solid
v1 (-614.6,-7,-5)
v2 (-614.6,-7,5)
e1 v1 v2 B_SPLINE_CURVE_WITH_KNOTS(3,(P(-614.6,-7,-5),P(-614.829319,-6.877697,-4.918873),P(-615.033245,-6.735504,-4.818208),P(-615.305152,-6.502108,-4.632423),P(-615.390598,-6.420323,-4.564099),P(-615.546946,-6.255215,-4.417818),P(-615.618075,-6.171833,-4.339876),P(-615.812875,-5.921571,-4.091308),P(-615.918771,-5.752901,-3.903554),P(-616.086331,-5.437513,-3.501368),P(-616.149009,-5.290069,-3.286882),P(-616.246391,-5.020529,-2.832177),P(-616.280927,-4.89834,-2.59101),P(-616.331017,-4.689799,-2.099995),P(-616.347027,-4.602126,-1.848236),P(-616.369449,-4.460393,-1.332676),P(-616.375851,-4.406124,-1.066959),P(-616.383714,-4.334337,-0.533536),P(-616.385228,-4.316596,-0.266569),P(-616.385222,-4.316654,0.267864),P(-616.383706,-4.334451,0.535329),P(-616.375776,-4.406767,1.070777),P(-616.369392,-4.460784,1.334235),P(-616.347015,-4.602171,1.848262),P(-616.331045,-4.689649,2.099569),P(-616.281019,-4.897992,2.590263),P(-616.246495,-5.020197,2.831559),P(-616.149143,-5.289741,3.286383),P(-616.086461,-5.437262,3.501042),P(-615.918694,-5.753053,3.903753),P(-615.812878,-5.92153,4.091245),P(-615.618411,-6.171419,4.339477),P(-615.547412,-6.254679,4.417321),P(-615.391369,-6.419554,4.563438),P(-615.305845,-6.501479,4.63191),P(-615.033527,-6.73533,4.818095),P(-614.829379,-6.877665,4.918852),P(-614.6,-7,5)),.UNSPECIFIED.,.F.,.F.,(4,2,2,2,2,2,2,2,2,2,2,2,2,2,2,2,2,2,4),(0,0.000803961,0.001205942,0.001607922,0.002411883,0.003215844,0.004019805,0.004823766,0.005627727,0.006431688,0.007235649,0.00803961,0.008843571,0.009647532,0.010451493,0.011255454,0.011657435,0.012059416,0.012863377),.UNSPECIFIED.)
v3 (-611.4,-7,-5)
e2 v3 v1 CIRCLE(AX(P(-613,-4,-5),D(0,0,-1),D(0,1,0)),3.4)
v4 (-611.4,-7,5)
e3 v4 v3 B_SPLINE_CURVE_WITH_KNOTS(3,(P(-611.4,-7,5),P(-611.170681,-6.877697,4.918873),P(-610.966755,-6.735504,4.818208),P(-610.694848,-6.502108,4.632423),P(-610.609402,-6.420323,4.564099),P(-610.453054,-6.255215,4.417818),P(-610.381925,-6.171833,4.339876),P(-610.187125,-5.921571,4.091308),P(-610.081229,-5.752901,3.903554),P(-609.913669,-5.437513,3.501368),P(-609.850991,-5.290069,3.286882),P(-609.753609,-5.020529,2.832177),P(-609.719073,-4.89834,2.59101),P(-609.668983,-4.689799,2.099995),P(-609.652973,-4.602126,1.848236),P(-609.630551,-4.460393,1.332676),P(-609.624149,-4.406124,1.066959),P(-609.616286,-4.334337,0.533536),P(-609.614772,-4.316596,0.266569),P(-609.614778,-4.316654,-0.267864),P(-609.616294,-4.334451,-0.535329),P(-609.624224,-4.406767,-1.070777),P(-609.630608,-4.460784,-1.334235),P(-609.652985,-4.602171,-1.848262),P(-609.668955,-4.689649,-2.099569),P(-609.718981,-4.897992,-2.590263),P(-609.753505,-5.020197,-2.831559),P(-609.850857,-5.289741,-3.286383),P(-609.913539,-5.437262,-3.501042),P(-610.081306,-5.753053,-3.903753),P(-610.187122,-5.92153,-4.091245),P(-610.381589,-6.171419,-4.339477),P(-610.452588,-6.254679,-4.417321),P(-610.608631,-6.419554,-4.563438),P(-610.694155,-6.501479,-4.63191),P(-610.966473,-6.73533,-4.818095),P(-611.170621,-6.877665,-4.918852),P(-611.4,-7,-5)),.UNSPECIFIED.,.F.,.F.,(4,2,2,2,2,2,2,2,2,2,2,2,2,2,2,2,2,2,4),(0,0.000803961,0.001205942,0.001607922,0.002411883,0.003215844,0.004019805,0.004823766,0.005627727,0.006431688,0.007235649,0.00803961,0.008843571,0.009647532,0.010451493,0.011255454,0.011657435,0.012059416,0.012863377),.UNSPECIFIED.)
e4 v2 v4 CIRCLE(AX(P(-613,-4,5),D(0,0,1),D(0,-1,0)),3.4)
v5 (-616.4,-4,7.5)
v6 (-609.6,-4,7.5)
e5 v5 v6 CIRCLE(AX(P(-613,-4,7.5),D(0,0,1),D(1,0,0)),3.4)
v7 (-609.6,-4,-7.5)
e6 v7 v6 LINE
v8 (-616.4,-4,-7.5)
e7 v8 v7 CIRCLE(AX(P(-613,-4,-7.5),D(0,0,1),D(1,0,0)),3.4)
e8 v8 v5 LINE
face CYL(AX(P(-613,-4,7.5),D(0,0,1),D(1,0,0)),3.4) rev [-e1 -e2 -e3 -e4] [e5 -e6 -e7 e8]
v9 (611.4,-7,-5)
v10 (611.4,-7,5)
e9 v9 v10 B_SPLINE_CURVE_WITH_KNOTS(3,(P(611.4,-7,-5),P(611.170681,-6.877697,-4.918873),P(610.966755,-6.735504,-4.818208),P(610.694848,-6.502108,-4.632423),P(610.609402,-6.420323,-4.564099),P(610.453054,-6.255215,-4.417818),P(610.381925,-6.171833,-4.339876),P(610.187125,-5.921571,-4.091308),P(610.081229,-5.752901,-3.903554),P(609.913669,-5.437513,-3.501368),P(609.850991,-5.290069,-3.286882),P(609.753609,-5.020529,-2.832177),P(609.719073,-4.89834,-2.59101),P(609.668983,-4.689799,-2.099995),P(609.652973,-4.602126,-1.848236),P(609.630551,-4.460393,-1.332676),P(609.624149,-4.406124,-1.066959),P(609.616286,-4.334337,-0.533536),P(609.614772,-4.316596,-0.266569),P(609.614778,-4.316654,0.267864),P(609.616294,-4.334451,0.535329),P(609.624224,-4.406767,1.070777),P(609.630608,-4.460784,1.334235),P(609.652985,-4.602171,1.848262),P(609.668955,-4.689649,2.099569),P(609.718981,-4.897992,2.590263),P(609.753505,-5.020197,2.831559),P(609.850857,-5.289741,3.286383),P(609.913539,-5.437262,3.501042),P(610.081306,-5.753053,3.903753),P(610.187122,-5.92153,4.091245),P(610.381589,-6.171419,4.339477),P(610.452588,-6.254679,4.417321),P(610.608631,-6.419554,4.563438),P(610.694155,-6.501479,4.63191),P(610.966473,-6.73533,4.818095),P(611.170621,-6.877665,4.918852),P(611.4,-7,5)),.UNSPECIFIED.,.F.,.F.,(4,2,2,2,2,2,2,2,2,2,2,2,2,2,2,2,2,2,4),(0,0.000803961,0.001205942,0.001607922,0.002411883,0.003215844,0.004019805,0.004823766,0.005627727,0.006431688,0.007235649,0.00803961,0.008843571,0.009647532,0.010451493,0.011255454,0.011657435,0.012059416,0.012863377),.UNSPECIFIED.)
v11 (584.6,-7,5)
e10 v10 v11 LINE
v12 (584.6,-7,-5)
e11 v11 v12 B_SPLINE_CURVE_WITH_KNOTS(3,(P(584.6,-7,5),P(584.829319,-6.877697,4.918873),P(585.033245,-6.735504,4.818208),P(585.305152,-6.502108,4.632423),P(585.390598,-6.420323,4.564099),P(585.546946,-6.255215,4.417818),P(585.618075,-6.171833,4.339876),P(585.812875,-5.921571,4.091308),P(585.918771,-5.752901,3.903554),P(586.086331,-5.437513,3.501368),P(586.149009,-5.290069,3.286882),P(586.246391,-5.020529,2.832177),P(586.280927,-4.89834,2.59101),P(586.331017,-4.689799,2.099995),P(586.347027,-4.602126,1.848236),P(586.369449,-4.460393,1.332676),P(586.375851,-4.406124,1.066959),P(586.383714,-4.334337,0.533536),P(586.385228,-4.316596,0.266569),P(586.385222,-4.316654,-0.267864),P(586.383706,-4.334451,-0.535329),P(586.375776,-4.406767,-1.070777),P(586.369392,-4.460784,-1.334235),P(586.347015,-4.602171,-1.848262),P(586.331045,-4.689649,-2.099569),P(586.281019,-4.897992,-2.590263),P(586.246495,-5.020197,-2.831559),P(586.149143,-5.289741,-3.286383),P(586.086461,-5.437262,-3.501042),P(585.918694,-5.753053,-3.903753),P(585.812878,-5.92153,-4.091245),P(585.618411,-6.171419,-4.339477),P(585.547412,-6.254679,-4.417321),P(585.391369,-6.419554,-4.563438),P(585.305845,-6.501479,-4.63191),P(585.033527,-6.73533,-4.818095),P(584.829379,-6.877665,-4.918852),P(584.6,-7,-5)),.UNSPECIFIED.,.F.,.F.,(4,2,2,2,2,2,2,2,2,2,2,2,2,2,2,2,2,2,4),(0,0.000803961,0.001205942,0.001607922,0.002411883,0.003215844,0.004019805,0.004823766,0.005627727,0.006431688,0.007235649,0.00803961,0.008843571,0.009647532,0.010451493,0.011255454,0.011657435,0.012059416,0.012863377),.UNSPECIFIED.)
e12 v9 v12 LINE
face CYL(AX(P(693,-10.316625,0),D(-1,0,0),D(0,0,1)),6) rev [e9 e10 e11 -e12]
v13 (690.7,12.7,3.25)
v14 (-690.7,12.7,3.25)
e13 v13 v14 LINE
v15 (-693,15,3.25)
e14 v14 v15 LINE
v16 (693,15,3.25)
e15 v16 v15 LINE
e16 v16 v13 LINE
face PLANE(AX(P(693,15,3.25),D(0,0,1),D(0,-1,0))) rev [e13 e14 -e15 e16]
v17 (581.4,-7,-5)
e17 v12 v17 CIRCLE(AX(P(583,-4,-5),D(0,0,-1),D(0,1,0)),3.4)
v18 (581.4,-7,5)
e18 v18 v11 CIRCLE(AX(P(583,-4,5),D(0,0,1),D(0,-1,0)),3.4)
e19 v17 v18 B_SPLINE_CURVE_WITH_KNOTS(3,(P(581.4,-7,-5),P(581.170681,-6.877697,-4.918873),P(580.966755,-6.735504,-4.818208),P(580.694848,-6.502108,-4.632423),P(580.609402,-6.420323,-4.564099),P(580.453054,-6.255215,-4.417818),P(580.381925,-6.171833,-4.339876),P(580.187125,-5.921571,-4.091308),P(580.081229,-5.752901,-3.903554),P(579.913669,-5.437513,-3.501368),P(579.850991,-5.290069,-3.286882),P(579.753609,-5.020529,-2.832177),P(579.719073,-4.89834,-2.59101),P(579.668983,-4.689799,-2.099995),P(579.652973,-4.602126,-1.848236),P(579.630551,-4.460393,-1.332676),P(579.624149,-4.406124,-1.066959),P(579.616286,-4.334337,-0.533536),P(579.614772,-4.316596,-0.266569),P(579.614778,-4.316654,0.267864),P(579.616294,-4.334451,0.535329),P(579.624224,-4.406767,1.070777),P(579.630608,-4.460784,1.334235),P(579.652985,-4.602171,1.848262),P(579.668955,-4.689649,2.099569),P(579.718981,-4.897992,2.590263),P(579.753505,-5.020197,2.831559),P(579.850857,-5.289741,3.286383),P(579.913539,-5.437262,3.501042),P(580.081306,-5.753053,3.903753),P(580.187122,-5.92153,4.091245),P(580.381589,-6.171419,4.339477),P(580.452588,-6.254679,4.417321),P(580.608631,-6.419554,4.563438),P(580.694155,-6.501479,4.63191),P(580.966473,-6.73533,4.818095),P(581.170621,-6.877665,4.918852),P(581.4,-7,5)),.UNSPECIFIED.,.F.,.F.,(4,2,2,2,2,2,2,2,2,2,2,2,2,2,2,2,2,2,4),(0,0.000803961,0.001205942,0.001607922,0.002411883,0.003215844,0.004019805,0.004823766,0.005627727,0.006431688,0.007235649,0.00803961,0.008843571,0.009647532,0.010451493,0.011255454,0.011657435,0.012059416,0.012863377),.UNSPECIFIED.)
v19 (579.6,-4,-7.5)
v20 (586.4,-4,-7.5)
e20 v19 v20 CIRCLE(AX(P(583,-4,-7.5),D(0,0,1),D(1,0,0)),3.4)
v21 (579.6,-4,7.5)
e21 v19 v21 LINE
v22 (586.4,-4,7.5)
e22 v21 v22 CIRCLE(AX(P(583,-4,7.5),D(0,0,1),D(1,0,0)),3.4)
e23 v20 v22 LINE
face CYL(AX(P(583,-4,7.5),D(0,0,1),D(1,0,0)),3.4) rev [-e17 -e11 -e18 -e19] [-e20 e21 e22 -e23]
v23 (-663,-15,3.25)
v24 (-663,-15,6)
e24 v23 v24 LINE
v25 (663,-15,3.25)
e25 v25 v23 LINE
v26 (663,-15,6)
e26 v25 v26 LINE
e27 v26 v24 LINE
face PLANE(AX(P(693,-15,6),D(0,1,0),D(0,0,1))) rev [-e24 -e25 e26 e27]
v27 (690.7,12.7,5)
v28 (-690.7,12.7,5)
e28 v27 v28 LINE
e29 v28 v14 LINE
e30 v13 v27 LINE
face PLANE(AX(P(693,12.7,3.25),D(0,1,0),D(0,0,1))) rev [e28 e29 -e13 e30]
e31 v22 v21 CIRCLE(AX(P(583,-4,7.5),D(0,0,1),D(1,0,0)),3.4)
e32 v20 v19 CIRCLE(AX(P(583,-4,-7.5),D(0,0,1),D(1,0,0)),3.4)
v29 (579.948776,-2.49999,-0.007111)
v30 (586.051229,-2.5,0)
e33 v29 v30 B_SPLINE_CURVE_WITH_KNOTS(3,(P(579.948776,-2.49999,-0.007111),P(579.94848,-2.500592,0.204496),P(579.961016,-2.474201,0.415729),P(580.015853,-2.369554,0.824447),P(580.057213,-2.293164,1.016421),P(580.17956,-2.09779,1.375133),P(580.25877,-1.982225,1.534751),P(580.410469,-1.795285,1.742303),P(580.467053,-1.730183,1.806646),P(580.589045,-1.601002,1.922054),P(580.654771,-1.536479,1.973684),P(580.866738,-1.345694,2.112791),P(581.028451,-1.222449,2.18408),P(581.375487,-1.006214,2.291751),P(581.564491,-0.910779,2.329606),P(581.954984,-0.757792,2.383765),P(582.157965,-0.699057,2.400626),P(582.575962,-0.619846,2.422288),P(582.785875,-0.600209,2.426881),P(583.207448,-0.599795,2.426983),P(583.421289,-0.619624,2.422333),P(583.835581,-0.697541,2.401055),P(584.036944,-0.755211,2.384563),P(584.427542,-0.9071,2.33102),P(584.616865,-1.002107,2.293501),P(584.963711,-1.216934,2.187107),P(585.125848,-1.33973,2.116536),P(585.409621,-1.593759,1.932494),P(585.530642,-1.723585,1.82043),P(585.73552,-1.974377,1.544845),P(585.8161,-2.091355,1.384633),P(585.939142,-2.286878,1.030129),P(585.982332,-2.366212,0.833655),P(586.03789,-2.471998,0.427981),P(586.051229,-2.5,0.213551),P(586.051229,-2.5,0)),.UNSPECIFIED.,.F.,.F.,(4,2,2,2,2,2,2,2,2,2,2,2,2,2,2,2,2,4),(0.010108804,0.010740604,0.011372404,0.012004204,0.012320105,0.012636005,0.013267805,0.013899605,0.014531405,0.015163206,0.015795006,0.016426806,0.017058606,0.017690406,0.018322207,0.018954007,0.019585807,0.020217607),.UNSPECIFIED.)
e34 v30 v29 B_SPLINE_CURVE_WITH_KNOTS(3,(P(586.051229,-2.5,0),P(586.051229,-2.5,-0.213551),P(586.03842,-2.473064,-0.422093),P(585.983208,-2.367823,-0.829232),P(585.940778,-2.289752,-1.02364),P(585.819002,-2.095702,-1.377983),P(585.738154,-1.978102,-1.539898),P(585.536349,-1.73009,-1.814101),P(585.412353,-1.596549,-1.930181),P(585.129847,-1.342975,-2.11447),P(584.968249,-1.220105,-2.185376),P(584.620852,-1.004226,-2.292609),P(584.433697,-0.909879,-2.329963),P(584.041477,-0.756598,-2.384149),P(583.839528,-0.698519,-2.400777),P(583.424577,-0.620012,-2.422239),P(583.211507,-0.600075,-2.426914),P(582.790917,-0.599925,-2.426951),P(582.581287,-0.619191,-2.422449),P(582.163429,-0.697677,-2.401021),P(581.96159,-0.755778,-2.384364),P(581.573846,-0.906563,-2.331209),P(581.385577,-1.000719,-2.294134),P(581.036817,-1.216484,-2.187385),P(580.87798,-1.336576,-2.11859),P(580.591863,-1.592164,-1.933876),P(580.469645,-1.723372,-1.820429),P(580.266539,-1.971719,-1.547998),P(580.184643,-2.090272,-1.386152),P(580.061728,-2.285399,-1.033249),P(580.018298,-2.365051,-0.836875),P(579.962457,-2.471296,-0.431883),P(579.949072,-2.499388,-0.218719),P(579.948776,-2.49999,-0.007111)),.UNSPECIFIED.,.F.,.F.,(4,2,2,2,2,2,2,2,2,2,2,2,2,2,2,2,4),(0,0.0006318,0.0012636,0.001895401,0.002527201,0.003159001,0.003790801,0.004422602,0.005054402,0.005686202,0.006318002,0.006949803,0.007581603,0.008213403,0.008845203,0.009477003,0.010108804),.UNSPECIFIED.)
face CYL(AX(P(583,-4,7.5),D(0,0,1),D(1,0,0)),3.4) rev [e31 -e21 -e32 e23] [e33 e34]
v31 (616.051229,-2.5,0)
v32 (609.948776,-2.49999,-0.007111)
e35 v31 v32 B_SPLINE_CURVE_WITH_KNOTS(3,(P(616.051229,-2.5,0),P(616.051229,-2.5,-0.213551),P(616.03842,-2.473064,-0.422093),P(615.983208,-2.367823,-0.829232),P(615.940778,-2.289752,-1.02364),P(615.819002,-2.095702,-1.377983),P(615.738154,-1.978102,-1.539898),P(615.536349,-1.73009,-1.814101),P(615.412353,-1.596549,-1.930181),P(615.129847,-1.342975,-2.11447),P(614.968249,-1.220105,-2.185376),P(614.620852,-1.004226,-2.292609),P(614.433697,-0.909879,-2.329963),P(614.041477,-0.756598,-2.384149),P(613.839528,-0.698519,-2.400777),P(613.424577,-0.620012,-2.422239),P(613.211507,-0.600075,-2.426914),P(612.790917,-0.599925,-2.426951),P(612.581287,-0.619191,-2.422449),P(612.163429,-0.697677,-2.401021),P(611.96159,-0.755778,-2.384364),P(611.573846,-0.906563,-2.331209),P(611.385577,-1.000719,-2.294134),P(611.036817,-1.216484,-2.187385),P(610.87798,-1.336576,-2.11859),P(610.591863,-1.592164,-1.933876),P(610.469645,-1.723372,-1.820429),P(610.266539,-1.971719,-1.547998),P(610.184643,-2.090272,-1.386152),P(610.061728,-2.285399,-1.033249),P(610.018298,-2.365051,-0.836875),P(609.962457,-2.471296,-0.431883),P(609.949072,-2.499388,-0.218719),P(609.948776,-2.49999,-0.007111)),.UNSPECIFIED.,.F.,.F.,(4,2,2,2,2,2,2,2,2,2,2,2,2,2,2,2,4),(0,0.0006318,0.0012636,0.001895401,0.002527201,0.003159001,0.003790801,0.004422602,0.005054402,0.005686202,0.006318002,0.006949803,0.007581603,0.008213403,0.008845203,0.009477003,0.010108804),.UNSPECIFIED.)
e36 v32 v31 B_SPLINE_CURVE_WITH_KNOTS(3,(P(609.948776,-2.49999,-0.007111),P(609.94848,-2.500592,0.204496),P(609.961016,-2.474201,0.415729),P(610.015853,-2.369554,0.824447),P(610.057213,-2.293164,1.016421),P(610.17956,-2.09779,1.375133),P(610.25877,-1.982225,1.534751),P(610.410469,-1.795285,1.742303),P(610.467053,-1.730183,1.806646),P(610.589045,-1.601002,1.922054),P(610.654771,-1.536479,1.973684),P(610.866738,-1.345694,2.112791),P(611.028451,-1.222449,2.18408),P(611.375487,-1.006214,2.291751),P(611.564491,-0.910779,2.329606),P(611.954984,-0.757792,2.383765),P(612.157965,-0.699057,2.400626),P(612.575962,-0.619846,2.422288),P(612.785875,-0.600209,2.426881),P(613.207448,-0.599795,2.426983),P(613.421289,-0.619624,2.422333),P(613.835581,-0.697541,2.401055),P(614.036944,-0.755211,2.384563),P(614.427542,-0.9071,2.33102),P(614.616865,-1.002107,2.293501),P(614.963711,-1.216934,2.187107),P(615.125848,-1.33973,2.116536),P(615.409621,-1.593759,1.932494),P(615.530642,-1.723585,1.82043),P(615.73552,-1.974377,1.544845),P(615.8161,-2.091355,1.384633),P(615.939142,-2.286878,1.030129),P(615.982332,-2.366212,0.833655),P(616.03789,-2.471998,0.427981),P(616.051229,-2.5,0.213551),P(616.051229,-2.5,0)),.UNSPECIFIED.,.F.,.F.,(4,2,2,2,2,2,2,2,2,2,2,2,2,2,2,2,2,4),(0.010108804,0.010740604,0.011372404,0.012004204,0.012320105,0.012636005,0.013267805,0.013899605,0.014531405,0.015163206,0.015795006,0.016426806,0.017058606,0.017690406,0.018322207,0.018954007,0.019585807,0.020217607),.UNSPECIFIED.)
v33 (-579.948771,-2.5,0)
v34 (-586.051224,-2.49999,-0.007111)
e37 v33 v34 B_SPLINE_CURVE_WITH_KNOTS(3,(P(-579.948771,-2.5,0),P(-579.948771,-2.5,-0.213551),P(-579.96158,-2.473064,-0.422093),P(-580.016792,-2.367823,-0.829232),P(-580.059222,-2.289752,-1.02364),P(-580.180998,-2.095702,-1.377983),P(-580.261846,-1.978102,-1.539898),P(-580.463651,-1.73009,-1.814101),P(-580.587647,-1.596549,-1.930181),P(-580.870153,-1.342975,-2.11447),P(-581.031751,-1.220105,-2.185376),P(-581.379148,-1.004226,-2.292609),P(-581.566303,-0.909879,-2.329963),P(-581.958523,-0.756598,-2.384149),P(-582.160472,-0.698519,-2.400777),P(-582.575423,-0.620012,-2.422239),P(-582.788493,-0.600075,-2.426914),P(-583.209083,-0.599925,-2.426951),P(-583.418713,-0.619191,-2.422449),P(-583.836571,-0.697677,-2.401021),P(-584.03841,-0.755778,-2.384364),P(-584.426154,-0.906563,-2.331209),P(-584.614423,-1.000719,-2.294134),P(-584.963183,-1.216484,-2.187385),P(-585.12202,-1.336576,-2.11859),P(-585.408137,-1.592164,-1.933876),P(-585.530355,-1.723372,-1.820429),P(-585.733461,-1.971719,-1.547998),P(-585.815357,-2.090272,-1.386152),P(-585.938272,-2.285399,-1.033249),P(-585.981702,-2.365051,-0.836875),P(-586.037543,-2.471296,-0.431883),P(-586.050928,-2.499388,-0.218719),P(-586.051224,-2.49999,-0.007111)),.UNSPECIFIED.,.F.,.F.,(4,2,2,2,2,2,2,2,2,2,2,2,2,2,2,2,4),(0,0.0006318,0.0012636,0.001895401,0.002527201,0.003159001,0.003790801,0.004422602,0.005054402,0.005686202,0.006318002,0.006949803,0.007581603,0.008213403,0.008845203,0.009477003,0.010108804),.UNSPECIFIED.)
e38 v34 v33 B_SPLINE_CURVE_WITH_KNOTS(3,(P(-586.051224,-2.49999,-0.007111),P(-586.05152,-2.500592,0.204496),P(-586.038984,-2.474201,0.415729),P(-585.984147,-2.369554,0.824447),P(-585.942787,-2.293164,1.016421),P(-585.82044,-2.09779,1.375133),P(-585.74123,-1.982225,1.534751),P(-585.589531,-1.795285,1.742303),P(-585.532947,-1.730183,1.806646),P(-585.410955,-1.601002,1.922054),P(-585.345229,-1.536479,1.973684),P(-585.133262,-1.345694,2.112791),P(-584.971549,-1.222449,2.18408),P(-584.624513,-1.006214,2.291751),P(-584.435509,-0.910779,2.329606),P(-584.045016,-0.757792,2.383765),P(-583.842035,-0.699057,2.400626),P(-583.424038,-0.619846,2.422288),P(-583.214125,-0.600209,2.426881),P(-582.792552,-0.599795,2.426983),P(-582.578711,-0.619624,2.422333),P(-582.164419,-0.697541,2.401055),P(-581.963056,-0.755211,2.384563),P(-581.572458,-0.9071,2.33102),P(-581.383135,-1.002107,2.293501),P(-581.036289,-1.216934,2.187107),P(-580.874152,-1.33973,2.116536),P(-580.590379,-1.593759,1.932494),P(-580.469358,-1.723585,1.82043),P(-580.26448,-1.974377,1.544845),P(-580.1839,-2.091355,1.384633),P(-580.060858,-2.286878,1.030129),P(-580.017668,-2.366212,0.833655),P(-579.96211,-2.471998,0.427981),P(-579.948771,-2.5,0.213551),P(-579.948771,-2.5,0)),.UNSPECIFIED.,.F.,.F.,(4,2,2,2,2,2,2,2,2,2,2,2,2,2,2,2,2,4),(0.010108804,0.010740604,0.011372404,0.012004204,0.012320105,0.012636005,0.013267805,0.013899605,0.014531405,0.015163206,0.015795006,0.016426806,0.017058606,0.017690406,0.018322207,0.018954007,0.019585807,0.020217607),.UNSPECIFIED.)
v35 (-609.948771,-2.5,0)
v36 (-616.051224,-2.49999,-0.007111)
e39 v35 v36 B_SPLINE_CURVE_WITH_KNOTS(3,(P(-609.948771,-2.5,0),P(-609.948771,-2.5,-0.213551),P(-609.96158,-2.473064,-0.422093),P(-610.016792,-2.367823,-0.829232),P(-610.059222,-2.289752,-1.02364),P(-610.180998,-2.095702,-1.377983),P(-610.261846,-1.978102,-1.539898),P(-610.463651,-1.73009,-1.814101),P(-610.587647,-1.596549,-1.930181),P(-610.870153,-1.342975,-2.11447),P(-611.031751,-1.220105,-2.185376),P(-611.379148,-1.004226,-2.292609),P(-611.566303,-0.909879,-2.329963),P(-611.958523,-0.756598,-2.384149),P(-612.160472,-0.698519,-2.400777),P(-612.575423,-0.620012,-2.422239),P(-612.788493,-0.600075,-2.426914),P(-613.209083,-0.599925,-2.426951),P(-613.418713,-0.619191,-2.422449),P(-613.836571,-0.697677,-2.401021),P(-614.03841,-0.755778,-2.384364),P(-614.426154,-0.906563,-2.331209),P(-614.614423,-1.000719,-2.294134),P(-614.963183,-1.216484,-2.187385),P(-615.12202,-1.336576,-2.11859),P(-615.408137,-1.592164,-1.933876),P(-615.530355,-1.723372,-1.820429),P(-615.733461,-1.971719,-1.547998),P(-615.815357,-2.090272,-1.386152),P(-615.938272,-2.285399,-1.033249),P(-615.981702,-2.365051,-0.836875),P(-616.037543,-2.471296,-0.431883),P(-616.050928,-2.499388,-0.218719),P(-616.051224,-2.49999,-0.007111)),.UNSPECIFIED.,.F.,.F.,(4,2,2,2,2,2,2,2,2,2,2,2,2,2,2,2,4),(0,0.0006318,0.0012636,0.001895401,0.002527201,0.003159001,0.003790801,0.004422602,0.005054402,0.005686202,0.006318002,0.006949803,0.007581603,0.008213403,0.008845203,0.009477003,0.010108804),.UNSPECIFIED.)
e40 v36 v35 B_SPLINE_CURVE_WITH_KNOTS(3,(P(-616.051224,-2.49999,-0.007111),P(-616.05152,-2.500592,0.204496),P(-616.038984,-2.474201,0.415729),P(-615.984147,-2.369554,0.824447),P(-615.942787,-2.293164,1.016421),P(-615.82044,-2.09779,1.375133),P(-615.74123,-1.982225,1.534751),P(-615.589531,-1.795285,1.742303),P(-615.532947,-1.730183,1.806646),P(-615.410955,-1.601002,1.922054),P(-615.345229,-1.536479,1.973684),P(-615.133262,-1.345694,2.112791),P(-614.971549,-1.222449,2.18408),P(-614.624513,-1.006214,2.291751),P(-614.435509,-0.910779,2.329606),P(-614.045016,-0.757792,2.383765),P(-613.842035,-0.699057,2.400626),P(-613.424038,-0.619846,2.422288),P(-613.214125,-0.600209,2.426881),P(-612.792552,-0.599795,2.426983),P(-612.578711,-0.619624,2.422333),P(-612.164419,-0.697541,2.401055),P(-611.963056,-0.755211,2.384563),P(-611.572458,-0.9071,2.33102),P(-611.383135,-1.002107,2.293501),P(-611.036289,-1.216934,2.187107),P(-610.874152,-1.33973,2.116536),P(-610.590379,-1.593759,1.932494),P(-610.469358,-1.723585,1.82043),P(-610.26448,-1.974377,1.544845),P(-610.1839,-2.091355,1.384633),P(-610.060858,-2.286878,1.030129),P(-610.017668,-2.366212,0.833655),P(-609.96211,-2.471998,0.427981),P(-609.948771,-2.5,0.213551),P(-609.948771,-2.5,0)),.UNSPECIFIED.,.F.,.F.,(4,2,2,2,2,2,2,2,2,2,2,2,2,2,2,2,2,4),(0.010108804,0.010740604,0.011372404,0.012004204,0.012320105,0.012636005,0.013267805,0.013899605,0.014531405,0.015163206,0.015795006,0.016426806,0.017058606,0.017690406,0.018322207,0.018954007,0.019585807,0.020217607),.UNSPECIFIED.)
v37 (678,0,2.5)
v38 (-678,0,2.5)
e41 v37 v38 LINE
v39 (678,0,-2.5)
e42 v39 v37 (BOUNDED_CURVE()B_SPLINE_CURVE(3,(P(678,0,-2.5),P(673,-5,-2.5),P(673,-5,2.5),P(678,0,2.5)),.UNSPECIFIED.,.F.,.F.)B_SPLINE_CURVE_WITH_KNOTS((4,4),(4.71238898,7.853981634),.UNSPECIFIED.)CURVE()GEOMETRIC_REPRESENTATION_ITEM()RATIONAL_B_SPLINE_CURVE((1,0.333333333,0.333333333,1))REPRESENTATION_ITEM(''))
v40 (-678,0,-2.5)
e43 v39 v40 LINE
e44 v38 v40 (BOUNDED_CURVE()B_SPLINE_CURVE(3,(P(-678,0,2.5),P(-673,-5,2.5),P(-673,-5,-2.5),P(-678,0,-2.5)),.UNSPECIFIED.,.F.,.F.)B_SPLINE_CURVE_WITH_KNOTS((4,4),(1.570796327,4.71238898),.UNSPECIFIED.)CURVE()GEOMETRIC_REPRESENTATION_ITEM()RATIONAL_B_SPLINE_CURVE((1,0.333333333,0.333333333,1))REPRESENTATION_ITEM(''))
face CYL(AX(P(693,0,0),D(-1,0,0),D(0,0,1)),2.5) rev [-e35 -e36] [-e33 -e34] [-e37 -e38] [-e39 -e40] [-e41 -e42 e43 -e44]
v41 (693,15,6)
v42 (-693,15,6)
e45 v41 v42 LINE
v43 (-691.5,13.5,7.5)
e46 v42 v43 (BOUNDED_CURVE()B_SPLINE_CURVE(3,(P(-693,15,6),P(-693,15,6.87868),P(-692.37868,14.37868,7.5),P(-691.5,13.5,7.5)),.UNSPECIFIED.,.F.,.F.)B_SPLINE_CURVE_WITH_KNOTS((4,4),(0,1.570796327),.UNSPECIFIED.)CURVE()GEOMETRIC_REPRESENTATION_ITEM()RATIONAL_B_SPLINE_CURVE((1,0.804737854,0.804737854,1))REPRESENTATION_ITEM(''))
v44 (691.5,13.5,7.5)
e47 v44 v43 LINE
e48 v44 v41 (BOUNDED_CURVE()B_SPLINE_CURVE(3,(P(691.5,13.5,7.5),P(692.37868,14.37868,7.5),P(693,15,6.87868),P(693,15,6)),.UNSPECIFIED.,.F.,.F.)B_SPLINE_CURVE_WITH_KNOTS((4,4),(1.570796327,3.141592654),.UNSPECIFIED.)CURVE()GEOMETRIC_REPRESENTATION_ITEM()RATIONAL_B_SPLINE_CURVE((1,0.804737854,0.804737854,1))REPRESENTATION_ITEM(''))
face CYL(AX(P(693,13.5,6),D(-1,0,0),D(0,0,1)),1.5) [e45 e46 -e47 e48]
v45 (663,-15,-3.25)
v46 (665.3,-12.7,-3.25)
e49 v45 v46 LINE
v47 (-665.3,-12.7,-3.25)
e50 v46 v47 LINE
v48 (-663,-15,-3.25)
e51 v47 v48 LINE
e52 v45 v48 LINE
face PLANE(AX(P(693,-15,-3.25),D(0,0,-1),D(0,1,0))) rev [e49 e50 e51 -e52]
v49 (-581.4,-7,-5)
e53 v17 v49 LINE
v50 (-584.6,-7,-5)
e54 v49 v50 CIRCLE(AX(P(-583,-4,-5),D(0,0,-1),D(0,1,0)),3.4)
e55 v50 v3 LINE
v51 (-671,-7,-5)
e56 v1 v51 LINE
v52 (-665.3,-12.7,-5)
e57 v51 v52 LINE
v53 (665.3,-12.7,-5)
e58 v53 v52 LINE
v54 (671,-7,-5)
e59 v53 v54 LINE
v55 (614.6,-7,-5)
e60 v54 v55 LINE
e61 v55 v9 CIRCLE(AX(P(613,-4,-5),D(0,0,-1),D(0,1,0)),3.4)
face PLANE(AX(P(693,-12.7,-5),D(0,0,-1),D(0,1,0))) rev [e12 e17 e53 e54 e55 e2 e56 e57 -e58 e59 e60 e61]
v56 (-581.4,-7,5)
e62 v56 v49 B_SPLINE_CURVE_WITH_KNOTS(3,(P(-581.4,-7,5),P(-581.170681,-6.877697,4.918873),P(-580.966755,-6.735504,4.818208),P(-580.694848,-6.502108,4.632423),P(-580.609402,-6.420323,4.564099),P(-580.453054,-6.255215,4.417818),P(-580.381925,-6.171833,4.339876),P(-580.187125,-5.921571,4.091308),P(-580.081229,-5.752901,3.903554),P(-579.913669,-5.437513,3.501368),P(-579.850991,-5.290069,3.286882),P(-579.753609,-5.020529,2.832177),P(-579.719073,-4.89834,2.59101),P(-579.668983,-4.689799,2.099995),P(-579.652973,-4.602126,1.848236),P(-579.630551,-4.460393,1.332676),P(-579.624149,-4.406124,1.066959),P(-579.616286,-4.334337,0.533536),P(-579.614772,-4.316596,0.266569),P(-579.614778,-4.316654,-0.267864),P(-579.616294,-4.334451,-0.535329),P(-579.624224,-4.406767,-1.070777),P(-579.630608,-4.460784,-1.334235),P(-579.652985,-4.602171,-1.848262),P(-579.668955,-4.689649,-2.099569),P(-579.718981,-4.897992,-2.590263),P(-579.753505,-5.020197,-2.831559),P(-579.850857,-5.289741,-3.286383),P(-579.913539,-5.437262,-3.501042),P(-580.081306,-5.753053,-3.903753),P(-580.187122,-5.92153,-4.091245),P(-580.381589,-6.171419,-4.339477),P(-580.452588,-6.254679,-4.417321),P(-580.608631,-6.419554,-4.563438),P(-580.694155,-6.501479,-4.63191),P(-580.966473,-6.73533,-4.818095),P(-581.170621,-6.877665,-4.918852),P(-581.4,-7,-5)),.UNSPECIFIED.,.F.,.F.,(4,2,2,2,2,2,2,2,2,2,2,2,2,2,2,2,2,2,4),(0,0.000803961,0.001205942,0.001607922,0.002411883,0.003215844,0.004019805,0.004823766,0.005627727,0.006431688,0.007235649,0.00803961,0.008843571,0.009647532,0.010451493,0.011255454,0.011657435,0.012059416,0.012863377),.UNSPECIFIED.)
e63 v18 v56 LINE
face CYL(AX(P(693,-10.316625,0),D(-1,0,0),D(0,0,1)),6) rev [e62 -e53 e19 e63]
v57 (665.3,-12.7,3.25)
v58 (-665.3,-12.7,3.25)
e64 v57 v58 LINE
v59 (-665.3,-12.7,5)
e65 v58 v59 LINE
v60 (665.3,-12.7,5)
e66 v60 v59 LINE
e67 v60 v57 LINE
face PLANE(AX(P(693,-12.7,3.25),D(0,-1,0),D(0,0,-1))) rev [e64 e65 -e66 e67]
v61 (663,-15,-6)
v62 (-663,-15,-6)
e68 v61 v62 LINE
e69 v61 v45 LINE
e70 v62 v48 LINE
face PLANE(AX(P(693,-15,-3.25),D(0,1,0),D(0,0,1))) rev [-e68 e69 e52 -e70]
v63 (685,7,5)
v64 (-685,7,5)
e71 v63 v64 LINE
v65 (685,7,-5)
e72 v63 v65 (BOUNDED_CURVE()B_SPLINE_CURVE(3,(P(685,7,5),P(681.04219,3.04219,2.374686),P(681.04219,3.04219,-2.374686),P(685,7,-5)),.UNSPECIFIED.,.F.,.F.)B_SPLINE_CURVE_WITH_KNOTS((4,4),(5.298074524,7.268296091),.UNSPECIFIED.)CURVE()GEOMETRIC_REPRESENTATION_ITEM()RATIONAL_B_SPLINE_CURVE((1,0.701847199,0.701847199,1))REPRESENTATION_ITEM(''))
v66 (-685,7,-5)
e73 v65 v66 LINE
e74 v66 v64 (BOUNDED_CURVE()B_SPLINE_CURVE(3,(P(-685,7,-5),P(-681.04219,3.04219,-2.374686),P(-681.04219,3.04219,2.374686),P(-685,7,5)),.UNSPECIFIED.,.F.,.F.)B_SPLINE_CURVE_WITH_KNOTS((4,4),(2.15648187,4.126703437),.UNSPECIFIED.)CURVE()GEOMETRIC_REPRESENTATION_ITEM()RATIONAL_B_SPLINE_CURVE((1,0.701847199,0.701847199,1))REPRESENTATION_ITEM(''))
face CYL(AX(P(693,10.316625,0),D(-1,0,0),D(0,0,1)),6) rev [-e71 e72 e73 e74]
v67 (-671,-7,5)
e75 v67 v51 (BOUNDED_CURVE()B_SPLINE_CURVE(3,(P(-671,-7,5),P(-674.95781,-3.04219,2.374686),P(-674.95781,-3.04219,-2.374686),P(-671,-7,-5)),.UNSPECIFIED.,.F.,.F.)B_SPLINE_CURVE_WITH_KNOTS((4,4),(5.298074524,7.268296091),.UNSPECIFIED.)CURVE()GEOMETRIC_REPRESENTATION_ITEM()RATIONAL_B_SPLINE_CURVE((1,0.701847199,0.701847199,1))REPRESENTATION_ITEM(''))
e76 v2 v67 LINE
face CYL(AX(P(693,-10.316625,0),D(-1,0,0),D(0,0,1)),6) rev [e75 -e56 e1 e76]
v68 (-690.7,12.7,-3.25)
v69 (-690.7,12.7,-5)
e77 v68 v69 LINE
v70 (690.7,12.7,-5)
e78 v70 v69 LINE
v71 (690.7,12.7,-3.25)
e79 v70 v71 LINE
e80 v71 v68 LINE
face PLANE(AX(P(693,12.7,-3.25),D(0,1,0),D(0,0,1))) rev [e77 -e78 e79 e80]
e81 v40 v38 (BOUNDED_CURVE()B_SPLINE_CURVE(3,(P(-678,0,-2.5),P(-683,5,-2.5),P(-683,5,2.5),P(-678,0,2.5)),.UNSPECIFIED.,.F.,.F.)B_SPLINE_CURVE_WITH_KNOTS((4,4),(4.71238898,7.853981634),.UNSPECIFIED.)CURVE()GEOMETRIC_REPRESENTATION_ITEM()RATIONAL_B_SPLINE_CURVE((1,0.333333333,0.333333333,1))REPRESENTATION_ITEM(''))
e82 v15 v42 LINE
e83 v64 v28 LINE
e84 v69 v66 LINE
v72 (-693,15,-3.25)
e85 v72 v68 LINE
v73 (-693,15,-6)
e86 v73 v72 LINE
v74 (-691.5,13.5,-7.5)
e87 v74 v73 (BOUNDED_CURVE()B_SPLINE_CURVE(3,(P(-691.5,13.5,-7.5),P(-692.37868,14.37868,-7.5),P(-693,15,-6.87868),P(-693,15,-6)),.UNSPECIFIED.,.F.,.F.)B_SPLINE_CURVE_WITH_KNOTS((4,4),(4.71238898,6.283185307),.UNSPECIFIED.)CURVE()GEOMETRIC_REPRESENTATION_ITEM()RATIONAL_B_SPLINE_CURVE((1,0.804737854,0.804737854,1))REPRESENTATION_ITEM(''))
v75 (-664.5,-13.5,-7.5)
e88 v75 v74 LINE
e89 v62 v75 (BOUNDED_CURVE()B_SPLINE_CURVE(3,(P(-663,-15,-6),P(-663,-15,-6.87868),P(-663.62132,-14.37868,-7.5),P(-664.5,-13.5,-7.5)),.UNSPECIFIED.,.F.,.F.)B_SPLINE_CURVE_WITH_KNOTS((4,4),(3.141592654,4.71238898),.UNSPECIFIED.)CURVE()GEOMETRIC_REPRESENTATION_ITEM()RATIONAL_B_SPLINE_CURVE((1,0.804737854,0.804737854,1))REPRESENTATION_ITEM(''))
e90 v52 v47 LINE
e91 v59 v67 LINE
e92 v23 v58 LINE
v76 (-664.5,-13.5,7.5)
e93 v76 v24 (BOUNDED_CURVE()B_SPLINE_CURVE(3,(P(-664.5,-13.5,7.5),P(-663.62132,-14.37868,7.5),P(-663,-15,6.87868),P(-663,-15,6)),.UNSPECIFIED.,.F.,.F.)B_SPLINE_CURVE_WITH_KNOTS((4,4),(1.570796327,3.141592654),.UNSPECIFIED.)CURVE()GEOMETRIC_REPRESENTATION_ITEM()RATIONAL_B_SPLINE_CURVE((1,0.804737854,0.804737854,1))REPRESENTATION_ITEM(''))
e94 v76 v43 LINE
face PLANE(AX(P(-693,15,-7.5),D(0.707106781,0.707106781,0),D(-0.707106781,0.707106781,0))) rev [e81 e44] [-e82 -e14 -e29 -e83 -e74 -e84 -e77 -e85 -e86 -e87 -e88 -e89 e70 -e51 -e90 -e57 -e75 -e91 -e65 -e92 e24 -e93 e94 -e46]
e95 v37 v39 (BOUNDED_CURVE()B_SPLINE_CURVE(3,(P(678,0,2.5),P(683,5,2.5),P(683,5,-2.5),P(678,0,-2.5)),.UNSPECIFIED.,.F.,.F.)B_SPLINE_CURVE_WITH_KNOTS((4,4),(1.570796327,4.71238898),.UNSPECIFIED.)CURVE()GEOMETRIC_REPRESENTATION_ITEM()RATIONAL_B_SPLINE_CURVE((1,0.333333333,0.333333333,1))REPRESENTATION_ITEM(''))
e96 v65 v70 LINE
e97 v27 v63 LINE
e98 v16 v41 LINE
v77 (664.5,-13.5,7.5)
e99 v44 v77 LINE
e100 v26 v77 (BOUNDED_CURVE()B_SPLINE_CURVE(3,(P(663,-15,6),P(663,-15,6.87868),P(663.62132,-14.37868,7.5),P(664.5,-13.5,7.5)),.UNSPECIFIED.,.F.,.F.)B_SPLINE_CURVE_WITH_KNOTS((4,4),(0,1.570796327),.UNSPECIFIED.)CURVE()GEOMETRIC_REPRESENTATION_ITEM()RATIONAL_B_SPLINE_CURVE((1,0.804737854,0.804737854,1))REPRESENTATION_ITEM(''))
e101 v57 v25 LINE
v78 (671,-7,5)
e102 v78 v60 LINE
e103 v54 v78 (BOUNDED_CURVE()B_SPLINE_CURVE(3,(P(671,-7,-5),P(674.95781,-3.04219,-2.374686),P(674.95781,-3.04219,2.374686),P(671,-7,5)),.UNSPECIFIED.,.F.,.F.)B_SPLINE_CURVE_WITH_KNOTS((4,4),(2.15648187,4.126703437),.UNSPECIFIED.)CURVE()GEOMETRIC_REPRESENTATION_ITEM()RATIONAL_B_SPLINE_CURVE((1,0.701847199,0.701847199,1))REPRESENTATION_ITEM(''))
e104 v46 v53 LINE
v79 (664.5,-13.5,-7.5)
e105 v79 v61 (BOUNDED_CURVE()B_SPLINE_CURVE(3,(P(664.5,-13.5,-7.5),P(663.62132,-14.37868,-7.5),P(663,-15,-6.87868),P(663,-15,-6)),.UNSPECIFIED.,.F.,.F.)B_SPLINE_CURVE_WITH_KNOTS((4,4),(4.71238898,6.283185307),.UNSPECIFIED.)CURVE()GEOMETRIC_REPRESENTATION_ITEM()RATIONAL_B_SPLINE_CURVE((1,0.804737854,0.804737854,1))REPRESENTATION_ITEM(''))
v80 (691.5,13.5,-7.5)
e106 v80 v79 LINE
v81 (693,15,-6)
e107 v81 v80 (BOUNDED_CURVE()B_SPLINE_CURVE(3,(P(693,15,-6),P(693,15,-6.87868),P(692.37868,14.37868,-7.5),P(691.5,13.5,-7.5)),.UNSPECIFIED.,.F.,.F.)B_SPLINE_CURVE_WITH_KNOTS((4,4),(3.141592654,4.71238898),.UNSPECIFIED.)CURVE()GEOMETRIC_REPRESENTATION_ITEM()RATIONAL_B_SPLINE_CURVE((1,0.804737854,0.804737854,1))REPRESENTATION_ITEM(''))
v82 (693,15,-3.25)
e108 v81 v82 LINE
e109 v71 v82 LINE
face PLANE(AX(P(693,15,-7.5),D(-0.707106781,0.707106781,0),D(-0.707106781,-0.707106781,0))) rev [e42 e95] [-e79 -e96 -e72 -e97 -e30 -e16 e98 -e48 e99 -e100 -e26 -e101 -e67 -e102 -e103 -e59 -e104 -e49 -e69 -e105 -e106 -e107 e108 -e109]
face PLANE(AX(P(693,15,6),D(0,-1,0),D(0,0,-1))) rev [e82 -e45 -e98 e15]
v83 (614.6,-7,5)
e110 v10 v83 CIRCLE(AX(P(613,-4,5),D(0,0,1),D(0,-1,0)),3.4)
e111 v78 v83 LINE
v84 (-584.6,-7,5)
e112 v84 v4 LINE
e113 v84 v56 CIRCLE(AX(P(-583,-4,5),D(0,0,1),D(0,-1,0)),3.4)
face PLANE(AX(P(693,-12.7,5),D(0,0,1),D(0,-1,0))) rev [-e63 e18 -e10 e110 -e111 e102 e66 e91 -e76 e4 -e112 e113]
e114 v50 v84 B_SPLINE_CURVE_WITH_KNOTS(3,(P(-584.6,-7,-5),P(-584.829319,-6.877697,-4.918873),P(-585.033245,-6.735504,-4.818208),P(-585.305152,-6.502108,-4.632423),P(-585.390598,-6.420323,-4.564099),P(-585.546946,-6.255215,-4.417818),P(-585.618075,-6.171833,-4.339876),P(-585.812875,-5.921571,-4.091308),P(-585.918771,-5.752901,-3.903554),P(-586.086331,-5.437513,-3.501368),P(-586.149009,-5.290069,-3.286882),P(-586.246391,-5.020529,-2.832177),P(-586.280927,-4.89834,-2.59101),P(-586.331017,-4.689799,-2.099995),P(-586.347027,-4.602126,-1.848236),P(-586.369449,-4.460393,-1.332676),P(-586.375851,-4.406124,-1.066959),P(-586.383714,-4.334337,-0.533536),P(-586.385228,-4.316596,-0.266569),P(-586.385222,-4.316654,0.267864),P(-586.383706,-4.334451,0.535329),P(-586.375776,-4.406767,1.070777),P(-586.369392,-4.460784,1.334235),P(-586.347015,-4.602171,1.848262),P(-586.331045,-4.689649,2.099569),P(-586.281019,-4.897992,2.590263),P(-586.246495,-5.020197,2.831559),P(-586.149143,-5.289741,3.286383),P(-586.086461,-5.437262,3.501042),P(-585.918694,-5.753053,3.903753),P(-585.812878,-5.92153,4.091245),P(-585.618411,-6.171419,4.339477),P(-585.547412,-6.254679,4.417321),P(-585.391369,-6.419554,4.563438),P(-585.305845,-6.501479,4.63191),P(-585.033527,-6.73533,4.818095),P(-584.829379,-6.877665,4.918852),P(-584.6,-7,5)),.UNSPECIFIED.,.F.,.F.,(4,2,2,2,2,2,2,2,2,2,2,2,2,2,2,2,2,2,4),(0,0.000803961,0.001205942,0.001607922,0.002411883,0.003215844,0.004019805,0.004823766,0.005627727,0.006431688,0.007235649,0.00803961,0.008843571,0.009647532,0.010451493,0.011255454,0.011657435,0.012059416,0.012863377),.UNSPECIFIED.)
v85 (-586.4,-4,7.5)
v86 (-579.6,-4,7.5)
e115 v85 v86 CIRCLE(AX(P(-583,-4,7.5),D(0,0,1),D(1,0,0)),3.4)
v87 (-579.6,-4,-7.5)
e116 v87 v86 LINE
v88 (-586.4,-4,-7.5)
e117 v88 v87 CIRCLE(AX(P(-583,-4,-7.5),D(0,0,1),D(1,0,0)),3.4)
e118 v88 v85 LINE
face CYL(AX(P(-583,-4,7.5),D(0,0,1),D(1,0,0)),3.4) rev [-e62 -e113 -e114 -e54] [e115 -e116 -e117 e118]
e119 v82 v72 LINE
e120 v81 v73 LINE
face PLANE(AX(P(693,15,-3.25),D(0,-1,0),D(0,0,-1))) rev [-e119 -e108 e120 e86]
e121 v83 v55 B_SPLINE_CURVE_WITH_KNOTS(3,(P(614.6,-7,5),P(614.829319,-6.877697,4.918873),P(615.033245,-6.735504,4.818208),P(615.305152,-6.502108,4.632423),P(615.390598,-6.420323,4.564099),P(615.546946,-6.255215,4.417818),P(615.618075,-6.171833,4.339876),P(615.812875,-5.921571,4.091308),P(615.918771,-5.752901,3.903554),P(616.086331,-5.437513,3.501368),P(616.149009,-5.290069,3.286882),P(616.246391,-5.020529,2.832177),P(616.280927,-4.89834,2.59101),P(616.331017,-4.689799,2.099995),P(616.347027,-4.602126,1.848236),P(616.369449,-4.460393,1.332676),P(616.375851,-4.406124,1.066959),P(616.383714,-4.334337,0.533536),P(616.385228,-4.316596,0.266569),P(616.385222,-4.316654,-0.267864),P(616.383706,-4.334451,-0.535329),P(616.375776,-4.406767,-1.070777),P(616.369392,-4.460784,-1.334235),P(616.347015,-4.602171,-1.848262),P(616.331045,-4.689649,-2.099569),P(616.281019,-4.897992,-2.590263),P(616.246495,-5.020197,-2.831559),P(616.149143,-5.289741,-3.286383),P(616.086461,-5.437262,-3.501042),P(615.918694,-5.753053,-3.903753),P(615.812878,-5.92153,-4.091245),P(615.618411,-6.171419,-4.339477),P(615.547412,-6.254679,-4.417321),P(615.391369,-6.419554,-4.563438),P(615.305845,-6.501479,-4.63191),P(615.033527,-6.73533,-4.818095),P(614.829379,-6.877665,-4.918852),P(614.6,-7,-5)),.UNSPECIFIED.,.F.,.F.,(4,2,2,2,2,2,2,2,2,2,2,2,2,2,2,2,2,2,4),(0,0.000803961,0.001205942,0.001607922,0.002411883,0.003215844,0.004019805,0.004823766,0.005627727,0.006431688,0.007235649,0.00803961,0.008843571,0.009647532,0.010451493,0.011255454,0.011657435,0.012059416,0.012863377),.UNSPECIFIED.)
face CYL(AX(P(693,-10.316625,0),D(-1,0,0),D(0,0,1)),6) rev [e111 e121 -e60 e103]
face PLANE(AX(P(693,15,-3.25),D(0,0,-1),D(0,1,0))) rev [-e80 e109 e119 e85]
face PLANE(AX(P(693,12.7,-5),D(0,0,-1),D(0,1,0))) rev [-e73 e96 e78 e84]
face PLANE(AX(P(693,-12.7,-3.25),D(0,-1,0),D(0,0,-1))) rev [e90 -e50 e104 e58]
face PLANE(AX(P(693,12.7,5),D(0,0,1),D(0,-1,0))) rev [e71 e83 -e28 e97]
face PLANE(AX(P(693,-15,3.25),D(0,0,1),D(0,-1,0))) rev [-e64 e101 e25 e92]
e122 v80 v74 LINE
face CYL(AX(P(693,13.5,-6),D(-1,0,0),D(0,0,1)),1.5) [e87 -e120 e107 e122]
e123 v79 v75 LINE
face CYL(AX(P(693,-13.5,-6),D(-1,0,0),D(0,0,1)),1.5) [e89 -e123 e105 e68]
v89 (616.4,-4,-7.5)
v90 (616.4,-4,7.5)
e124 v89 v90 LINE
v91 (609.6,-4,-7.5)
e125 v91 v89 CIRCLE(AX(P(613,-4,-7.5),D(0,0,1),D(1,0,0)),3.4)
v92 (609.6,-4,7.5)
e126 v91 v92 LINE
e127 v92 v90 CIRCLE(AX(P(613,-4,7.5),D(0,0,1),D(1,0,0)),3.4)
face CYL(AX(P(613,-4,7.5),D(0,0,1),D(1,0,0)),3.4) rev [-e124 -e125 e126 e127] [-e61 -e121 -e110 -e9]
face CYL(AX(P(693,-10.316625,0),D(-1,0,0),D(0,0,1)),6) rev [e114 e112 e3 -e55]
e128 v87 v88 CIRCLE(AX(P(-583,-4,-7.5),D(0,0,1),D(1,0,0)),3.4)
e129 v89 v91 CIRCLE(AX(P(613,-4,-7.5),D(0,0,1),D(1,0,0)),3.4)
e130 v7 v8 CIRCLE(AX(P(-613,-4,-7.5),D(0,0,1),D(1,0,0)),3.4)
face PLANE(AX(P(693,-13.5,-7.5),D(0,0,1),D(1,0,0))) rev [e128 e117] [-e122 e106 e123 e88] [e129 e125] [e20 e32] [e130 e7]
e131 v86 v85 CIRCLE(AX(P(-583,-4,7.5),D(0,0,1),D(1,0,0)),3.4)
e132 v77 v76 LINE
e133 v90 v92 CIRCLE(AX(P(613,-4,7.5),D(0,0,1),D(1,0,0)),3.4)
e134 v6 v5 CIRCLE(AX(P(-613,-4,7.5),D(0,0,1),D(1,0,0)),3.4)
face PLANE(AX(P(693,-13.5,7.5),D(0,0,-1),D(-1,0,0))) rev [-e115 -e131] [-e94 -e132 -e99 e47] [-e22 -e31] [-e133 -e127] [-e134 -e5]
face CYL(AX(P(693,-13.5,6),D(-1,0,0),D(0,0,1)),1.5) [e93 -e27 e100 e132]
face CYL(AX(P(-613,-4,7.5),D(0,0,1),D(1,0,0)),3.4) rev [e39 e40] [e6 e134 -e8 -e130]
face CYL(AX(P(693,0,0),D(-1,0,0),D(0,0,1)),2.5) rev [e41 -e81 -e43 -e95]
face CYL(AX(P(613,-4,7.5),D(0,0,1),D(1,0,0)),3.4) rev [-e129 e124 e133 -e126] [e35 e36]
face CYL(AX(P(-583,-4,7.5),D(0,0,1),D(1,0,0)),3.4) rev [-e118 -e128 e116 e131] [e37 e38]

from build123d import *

# Parameters (mm, degrees)
SKETCH11_R          = 2.5
MEMBER_1_DEPTH      = 1386
CUT_EXTRUDE_1_DEPTH = 694.324599304
HOLE_WIZARD_M8_1_D  = 6.8


with BuildPart() as part:
    # Sketch11 → Member 1 (new body)
    with BuildSketch(Plane(origin=(-693, 0, 0), x_dir=(0, 0, -1), z_dir=(1, 0, 0))):
        with BuildLine():
            Line((-6, -15), (-3.25, -15))
            Line((-3.25, -15), (-3.25, -12.7))
            Line((-3.25, -12.7), (-5, -12.7))
            Line((-5, -12.7), (-5, -7))
            ThreePointArc((-5, -7), (0, -4.31662479), (5, -7))
            Line((5, -7), (5, -12.7))
            Line((5, -12.7), (3.25, -12.7))
            Line((3.25, -12.7), (3.25, -15))
            Line((3.25, -15), (6, -15))
            ThreePointArc((6, -15), (7.060660172, -14.560660172), (7.5, -13.5))
            Line((7.5, -13.5), (7.5, 13.5))
            ThreePointArc((7.5, 13.5), (7.060660172, 14.560660172), (6, 15))
            Line((6, 15), (3.25, 15))
            Line((3.25, 15), (3.25, 12.7))
            Line((3.25, 12.7), (5, 12.7))
            Line((5, 12.7), (5, 7))
            ThreePointArc((5, 7), (0, 4.31662479), (-5, 7))
            Line((-5, 7), (-5, 12.7))
            Line((-5, 12.7), (-3.25, 12.7))
            Line((-3.25, 12.7), (-3.25, 15))
            Line((-3.25, 15), (-6, 15))
            ThreePointArc((-6, 15), (-7.060660172, 14.560660172), (-7.5, 13.5))
            Line((-7.5, 13.5), (-7.5, -13.5))
            ThreePointArc((-7.5, -13.5), (-7.060660172, -14.560660172), (-6, -15))
        make_face()
        Circle(SKETCH11_R, mode=Mode.SUBTRACT)
    extrude(amount=MEMBER_1_DEPTH)

    # 草图4 → 切除-拉伸1 (cut, through all)
    with BuildSketch(Plane.XY.offset(7.5)):
        Polygon((-693, 15), (-663, -15), (-693, -15), align=None)
        Polygon((693, -15), (693, 15), (663, -15), align=None)
    extrude(amount=-CUT_EXTRUDE_1_DEPTH, mode=Mode.SUBTRACT)

    # M8 螺纹孔1 (through all)
    with Locations(Plane.XY.offset(7.5)):
        with Locations((-613, -4), (-583, -4), (583, -4), (613, -4)):
            Hole(HOLE_WIZARD_M8_1_D / 2)


solid = part.part
